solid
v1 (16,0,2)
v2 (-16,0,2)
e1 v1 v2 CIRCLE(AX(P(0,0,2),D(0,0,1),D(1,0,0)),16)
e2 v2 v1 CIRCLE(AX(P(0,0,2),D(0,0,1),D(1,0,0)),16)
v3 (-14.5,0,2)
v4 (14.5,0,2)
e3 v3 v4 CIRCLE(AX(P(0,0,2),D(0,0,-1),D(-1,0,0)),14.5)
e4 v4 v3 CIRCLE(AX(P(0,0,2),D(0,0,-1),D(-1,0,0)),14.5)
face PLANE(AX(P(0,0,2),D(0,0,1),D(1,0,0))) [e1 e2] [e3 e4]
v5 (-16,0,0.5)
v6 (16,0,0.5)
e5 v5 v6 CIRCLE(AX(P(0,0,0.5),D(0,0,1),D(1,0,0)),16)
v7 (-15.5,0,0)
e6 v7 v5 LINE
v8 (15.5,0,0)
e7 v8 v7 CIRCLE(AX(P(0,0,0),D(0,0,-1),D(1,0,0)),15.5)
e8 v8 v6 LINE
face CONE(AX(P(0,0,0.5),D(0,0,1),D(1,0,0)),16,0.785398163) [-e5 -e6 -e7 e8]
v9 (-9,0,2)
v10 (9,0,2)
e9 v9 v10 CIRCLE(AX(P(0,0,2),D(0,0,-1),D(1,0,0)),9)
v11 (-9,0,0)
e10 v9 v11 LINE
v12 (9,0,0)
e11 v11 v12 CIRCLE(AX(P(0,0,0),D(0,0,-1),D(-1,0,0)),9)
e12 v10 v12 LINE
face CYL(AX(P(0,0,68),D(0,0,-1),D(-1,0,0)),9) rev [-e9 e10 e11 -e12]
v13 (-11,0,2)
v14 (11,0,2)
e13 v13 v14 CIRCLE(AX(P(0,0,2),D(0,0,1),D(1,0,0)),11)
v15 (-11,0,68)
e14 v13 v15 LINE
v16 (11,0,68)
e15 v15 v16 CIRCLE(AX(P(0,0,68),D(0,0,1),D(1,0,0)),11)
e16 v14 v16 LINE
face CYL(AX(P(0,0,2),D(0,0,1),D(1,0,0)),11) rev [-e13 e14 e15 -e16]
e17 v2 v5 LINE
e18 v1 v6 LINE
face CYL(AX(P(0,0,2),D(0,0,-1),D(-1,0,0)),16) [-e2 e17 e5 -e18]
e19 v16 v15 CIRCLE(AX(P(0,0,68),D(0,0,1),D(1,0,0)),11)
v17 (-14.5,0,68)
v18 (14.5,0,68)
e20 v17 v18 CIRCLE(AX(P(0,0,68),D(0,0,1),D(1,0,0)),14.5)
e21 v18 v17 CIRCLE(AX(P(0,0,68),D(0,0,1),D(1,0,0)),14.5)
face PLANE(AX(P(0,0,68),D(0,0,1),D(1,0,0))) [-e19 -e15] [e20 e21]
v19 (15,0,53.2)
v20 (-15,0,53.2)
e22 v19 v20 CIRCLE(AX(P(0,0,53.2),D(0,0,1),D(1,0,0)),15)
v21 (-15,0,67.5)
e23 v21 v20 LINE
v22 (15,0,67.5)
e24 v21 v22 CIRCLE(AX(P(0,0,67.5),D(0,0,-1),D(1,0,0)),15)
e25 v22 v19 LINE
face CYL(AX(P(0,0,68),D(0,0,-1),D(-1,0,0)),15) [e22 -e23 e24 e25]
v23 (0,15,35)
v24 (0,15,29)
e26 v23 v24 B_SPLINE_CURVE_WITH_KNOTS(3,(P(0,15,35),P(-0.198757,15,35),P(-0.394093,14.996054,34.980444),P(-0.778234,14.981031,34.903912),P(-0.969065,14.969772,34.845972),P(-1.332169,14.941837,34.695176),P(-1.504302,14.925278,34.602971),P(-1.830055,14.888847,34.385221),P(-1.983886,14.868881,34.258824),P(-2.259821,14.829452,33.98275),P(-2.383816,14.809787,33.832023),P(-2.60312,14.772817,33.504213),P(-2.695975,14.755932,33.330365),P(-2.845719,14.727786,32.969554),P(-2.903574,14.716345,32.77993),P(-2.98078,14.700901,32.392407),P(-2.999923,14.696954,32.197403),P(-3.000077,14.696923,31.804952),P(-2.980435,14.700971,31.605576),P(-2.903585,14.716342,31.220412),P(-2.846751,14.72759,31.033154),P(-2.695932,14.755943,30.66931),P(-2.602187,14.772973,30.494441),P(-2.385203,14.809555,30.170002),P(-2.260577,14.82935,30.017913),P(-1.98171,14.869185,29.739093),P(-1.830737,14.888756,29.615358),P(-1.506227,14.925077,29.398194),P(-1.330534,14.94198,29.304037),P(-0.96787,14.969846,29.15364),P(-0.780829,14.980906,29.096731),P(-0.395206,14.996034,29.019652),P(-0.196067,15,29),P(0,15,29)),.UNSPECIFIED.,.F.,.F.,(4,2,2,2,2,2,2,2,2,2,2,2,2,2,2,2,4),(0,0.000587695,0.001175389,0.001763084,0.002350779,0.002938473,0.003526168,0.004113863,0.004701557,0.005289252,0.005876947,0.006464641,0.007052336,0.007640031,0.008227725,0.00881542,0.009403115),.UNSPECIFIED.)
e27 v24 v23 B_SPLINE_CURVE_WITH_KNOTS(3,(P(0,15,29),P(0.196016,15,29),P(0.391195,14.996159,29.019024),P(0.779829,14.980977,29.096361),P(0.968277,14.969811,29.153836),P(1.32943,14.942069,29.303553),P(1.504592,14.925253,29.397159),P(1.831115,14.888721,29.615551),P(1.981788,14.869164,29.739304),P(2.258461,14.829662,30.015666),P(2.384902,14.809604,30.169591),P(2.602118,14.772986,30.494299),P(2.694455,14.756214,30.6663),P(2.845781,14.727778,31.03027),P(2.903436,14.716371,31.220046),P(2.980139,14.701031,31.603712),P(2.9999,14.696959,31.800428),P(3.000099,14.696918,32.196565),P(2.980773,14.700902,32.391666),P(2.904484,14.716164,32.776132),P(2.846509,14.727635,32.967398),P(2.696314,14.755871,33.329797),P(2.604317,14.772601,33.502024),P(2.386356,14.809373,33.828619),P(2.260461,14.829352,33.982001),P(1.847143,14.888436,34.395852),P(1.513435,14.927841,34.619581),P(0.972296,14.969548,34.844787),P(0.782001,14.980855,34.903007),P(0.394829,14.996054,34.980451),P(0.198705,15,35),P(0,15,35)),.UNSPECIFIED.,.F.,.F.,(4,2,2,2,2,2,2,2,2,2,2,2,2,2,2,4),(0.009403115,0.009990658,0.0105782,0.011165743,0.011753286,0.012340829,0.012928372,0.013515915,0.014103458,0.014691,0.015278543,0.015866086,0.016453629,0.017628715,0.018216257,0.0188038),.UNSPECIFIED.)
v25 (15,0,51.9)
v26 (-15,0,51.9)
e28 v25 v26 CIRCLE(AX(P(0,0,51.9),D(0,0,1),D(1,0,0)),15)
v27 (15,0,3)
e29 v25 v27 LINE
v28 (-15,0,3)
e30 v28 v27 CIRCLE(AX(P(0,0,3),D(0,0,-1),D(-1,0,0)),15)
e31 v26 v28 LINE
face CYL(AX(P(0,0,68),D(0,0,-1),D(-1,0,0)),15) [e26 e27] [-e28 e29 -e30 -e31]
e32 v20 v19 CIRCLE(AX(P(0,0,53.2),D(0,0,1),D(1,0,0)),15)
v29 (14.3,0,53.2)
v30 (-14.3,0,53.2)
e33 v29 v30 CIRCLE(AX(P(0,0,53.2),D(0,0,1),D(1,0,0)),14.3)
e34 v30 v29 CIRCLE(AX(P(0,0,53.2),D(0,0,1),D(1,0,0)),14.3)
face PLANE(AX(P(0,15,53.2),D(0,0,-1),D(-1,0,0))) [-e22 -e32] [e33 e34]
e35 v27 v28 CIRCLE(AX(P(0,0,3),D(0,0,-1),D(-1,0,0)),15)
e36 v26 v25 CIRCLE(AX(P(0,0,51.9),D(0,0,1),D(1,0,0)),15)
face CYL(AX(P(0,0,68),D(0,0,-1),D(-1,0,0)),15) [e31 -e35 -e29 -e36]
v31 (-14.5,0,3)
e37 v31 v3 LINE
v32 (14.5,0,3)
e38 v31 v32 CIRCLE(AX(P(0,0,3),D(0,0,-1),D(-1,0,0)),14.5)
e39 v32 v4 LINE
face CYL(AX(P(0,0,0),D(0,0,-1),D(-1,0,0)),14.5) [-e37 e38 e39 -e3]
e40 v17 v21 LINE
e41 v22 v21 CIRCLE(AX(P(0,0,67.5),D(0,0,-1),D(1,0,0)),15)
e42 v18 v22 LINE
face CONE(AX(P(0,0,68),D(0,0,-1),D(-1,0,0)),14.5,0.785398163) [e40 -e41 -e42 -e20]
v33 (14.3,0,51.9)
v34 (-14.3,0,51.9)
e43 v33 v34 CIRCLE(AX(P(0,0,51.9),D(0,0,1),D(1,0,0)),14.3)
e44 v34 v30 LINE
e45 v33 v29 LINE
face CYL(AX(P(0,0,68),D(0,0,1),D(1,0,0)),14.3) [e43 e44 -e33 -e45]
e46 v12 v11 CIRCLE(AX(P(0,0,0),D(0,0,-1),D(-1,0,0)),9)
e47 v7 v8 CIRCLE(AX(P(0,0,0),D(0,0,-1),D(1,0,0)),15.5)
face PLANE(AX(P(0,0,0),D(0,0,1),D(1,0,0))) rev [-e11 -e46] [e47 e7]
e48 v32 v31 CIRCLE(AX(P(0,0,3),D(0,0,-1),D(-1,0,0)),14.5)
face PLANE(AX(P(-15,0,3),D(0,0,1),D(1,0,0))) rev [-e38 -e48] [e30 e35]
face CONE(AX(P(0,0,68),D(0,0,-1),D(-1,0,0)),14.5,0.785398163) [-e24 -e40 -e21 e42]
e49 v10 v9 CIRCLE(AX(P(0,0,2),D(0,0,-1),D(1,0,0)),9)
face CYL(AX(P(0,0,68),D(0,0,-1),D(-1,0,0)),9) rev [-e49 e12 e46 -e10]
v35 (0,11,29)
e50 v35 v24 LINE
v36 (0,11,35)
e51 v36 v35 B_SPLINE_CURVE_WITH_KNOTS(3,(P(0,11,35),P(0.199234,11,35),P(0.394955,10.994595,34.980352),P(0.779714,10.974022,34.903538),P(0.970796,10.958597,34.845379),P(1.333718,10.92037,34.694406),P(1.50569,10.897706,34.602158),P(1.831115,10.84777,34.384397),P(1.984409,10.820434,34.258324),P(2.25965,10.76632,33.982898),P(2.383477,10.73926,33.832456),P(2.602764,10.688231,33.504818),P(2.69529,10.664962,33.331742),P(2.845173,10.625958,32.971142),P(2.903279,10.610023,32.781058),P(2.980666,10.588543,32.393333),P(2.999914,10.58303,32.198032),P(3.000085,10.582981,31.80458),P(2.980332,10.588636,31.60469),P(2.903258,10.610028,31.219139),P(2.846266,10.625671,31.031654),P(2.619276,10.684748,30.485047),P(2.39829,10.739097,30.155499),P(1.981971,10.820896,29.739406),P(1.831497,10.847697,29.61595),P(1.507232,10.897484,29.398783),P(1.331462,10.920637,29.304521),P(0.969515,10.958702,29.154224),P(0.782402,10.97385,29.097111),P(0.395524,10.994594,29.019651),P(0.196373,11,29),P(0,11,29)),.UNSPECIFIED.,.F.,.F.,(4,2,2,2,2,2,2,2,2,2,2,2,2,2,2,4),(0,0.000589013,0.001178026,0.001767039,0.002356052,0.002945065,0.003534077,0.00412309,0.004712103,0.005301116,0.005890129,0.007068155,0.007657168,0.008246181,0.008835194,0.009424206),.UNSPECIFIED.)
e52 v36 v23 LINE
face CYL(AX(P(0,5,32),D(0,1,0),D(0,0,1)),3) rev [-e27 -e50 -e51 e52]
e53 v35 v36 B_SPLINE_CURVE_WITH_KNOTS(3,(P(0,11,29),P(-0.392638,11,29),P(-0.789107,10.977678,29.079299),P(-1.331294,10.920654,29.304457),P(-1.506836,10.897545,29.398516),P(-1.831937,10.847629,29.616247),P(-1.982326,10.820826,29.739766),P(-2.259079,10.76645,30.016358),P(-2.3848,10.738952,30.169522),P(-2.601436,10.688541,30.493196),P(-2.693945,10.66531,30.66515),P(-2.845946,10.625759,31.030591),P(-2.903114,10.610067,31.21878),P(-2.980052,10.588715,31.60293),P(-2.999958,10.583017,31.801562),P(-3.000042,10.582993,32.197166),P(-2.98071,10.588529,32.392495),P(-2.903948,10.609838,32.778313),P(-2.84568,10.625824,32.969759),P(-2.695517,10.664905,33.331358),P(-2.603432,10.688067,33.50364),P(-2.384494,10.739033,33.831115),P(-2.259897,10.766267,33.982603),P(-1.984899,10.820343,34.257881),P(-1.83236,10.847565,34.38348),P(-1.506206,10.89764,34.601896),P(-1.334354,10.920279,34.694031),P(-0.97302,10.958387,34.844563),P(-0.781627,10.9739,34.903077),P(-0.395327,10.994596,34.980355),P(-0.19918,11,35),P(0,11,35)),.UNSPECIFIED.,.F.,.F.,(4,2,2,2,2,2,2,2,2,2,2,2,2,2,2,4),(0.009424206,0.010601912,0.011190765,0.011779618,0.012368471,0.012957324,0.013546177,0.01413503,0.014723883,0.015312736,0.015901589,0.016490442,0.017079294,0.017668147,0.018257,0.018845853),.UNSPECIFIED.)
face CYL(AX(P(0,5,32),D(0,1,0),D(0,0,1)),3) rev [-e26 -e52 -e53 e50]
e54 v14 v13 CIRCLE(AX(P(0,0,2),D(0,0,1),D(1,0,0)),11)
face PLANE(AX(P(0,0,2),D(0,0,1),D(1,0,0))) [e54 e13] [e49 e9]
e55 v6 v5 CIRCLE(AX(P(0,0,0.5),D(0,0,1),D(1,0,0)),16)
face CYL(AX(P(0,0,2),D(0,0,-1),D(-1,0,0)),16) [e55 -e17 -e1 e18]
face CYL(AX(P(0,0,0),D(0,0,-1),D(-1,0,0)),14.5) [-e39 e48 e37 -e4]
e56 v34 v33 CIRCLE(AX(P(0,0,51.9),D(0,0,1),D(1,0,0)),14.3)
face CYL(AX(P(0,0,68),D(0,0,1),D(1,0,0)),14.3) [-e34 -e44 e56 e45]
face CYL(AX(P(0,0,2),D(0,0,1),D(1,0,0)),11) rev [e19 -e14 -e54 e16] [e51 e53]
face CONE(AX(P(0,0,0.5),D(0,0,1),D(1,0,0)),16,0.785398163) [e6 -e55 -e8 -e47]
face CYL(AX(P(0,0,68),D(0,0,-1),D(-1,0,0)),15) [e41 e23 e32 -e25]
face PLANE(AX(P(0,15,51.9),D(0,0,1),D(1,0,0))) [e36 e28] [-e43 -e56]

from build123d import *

# Parameters (mm, degrees)
SKETCH_1_R          = 16
EXTRUDE_1_DEPTH     = 2
SKETCH_2_R          = 15
EXTRUDE_2_DEPTH     = 66
SKETCH_3_R          = 9
CUT_EXTRUDE_1_DEPTH = 72.665891469
SKETCH_5_R          = 11
CUT_EXTRUDE_2_DEPTH = 66
SKETCH_8_R          = 3
CUT_EXTRUDE_3_DEPTH = 10
SKETCH_9_W          = 1.3
SKETCH_9_H          = 0.7
CHAMFER_1_SIZE      = 0.5
SKETCH_10_W         = 0.5
SKETCH_10_H         = 1


with BuildPart() as part:
    # 草图1 → 凸台-拉伸1 (new body)
    with BuildSketch(Plane.XY):
        Circle(SKETCH_1_R)
    extrude(amount=EXTRUDE_1_DEPTH)

    # 草图2 → 凸台-拉伸2 (add)
    with BuildSketch(Plane.XY.offset(2)):
        Circle(SKETCH_2_R)
    extrude(amount=EXTRUDE_2_DEPTH)

    # 草图3 → 切除-拉伸1 (cut, through all)
    with BuildSketch(Plane(origin=(0, 0, 0), x_dir=(-1, 0, 0), z_dir=(0, 0, -1))):
        Circle(SKETCH_3_R)
    extrude(amount=-CUT_EXTRUDE_1_DEPTH, mode=Mode.SUBTRACT)

    # 草图5 → 切除-拉伸2 (cut)
    with BuildSketch(Plane.XY.offset(68)):
        Circle(SKETCH_5_R)
    extrude(amount=-CUT_EXTRUDE_2_DEPTH, mode=Mode.SUBTRACT)

    # 草图8 → 切除-拉伸3 (cut)
    with BuildSketch(Plane(origin=(0, 15, 0), x_dir=(1, 0, 0), z_dir=(0, 1, 0))):
        with Locations(Location((0, -32, 0), (0, 0, 270))):
            Circle(SKETCH_8_R)
    extrude(amount=-CUT_EXTRUDE_3_DEPTH, mode=Mode.SUBTRACT)

    # 草图9 → 切除-旋转1 (revolve, cut)
    with BuildSketch(Plane(origin=(0, 0, 0), x_dir=(0, 0, -1), z_dir=(1, 0, 0)), mode=Mode.PRIVATE) as cut_revolve_1_sk:
        with Locations((-52.55, 14.65)):
            Rectangle(SKETCH_9_W, SKETCH_9_H)
    revolve(cut_revolve_1_sk.sketch.rotate(Axis((0, 0, 68), (0, 0, -1)), 90), axis=Axis((0, 0, 68), (0, 0, -1)), mode=Mode.SUBTRACT)

    # 倒角1
    chamfer_1_edges = [part.edges().sort_by_distance(p)[0] for p in [
        (-16, 0, 0),
        (-15, 0, 68),
    ]]
    chamfer(chamfer_1_edges, length=CHAMFER_1_SIZE)

    # 草图10 → 切除-旋转2 (revolve, cut)
    with BuildSketch(Plane(origin=(0, 0, 0), x_dir=(1, 0, 0), z_dir=(0, 1, 0))):
        with Locations((-14.75, -2.5)):
            Rectangle(SKETCH_10_W, SKETCH_10_H)
    revolve(axis=Axis((0, 0, 0), (0, 0, 1)), mode=Mode.SUBTRACT)


solid = part.part
